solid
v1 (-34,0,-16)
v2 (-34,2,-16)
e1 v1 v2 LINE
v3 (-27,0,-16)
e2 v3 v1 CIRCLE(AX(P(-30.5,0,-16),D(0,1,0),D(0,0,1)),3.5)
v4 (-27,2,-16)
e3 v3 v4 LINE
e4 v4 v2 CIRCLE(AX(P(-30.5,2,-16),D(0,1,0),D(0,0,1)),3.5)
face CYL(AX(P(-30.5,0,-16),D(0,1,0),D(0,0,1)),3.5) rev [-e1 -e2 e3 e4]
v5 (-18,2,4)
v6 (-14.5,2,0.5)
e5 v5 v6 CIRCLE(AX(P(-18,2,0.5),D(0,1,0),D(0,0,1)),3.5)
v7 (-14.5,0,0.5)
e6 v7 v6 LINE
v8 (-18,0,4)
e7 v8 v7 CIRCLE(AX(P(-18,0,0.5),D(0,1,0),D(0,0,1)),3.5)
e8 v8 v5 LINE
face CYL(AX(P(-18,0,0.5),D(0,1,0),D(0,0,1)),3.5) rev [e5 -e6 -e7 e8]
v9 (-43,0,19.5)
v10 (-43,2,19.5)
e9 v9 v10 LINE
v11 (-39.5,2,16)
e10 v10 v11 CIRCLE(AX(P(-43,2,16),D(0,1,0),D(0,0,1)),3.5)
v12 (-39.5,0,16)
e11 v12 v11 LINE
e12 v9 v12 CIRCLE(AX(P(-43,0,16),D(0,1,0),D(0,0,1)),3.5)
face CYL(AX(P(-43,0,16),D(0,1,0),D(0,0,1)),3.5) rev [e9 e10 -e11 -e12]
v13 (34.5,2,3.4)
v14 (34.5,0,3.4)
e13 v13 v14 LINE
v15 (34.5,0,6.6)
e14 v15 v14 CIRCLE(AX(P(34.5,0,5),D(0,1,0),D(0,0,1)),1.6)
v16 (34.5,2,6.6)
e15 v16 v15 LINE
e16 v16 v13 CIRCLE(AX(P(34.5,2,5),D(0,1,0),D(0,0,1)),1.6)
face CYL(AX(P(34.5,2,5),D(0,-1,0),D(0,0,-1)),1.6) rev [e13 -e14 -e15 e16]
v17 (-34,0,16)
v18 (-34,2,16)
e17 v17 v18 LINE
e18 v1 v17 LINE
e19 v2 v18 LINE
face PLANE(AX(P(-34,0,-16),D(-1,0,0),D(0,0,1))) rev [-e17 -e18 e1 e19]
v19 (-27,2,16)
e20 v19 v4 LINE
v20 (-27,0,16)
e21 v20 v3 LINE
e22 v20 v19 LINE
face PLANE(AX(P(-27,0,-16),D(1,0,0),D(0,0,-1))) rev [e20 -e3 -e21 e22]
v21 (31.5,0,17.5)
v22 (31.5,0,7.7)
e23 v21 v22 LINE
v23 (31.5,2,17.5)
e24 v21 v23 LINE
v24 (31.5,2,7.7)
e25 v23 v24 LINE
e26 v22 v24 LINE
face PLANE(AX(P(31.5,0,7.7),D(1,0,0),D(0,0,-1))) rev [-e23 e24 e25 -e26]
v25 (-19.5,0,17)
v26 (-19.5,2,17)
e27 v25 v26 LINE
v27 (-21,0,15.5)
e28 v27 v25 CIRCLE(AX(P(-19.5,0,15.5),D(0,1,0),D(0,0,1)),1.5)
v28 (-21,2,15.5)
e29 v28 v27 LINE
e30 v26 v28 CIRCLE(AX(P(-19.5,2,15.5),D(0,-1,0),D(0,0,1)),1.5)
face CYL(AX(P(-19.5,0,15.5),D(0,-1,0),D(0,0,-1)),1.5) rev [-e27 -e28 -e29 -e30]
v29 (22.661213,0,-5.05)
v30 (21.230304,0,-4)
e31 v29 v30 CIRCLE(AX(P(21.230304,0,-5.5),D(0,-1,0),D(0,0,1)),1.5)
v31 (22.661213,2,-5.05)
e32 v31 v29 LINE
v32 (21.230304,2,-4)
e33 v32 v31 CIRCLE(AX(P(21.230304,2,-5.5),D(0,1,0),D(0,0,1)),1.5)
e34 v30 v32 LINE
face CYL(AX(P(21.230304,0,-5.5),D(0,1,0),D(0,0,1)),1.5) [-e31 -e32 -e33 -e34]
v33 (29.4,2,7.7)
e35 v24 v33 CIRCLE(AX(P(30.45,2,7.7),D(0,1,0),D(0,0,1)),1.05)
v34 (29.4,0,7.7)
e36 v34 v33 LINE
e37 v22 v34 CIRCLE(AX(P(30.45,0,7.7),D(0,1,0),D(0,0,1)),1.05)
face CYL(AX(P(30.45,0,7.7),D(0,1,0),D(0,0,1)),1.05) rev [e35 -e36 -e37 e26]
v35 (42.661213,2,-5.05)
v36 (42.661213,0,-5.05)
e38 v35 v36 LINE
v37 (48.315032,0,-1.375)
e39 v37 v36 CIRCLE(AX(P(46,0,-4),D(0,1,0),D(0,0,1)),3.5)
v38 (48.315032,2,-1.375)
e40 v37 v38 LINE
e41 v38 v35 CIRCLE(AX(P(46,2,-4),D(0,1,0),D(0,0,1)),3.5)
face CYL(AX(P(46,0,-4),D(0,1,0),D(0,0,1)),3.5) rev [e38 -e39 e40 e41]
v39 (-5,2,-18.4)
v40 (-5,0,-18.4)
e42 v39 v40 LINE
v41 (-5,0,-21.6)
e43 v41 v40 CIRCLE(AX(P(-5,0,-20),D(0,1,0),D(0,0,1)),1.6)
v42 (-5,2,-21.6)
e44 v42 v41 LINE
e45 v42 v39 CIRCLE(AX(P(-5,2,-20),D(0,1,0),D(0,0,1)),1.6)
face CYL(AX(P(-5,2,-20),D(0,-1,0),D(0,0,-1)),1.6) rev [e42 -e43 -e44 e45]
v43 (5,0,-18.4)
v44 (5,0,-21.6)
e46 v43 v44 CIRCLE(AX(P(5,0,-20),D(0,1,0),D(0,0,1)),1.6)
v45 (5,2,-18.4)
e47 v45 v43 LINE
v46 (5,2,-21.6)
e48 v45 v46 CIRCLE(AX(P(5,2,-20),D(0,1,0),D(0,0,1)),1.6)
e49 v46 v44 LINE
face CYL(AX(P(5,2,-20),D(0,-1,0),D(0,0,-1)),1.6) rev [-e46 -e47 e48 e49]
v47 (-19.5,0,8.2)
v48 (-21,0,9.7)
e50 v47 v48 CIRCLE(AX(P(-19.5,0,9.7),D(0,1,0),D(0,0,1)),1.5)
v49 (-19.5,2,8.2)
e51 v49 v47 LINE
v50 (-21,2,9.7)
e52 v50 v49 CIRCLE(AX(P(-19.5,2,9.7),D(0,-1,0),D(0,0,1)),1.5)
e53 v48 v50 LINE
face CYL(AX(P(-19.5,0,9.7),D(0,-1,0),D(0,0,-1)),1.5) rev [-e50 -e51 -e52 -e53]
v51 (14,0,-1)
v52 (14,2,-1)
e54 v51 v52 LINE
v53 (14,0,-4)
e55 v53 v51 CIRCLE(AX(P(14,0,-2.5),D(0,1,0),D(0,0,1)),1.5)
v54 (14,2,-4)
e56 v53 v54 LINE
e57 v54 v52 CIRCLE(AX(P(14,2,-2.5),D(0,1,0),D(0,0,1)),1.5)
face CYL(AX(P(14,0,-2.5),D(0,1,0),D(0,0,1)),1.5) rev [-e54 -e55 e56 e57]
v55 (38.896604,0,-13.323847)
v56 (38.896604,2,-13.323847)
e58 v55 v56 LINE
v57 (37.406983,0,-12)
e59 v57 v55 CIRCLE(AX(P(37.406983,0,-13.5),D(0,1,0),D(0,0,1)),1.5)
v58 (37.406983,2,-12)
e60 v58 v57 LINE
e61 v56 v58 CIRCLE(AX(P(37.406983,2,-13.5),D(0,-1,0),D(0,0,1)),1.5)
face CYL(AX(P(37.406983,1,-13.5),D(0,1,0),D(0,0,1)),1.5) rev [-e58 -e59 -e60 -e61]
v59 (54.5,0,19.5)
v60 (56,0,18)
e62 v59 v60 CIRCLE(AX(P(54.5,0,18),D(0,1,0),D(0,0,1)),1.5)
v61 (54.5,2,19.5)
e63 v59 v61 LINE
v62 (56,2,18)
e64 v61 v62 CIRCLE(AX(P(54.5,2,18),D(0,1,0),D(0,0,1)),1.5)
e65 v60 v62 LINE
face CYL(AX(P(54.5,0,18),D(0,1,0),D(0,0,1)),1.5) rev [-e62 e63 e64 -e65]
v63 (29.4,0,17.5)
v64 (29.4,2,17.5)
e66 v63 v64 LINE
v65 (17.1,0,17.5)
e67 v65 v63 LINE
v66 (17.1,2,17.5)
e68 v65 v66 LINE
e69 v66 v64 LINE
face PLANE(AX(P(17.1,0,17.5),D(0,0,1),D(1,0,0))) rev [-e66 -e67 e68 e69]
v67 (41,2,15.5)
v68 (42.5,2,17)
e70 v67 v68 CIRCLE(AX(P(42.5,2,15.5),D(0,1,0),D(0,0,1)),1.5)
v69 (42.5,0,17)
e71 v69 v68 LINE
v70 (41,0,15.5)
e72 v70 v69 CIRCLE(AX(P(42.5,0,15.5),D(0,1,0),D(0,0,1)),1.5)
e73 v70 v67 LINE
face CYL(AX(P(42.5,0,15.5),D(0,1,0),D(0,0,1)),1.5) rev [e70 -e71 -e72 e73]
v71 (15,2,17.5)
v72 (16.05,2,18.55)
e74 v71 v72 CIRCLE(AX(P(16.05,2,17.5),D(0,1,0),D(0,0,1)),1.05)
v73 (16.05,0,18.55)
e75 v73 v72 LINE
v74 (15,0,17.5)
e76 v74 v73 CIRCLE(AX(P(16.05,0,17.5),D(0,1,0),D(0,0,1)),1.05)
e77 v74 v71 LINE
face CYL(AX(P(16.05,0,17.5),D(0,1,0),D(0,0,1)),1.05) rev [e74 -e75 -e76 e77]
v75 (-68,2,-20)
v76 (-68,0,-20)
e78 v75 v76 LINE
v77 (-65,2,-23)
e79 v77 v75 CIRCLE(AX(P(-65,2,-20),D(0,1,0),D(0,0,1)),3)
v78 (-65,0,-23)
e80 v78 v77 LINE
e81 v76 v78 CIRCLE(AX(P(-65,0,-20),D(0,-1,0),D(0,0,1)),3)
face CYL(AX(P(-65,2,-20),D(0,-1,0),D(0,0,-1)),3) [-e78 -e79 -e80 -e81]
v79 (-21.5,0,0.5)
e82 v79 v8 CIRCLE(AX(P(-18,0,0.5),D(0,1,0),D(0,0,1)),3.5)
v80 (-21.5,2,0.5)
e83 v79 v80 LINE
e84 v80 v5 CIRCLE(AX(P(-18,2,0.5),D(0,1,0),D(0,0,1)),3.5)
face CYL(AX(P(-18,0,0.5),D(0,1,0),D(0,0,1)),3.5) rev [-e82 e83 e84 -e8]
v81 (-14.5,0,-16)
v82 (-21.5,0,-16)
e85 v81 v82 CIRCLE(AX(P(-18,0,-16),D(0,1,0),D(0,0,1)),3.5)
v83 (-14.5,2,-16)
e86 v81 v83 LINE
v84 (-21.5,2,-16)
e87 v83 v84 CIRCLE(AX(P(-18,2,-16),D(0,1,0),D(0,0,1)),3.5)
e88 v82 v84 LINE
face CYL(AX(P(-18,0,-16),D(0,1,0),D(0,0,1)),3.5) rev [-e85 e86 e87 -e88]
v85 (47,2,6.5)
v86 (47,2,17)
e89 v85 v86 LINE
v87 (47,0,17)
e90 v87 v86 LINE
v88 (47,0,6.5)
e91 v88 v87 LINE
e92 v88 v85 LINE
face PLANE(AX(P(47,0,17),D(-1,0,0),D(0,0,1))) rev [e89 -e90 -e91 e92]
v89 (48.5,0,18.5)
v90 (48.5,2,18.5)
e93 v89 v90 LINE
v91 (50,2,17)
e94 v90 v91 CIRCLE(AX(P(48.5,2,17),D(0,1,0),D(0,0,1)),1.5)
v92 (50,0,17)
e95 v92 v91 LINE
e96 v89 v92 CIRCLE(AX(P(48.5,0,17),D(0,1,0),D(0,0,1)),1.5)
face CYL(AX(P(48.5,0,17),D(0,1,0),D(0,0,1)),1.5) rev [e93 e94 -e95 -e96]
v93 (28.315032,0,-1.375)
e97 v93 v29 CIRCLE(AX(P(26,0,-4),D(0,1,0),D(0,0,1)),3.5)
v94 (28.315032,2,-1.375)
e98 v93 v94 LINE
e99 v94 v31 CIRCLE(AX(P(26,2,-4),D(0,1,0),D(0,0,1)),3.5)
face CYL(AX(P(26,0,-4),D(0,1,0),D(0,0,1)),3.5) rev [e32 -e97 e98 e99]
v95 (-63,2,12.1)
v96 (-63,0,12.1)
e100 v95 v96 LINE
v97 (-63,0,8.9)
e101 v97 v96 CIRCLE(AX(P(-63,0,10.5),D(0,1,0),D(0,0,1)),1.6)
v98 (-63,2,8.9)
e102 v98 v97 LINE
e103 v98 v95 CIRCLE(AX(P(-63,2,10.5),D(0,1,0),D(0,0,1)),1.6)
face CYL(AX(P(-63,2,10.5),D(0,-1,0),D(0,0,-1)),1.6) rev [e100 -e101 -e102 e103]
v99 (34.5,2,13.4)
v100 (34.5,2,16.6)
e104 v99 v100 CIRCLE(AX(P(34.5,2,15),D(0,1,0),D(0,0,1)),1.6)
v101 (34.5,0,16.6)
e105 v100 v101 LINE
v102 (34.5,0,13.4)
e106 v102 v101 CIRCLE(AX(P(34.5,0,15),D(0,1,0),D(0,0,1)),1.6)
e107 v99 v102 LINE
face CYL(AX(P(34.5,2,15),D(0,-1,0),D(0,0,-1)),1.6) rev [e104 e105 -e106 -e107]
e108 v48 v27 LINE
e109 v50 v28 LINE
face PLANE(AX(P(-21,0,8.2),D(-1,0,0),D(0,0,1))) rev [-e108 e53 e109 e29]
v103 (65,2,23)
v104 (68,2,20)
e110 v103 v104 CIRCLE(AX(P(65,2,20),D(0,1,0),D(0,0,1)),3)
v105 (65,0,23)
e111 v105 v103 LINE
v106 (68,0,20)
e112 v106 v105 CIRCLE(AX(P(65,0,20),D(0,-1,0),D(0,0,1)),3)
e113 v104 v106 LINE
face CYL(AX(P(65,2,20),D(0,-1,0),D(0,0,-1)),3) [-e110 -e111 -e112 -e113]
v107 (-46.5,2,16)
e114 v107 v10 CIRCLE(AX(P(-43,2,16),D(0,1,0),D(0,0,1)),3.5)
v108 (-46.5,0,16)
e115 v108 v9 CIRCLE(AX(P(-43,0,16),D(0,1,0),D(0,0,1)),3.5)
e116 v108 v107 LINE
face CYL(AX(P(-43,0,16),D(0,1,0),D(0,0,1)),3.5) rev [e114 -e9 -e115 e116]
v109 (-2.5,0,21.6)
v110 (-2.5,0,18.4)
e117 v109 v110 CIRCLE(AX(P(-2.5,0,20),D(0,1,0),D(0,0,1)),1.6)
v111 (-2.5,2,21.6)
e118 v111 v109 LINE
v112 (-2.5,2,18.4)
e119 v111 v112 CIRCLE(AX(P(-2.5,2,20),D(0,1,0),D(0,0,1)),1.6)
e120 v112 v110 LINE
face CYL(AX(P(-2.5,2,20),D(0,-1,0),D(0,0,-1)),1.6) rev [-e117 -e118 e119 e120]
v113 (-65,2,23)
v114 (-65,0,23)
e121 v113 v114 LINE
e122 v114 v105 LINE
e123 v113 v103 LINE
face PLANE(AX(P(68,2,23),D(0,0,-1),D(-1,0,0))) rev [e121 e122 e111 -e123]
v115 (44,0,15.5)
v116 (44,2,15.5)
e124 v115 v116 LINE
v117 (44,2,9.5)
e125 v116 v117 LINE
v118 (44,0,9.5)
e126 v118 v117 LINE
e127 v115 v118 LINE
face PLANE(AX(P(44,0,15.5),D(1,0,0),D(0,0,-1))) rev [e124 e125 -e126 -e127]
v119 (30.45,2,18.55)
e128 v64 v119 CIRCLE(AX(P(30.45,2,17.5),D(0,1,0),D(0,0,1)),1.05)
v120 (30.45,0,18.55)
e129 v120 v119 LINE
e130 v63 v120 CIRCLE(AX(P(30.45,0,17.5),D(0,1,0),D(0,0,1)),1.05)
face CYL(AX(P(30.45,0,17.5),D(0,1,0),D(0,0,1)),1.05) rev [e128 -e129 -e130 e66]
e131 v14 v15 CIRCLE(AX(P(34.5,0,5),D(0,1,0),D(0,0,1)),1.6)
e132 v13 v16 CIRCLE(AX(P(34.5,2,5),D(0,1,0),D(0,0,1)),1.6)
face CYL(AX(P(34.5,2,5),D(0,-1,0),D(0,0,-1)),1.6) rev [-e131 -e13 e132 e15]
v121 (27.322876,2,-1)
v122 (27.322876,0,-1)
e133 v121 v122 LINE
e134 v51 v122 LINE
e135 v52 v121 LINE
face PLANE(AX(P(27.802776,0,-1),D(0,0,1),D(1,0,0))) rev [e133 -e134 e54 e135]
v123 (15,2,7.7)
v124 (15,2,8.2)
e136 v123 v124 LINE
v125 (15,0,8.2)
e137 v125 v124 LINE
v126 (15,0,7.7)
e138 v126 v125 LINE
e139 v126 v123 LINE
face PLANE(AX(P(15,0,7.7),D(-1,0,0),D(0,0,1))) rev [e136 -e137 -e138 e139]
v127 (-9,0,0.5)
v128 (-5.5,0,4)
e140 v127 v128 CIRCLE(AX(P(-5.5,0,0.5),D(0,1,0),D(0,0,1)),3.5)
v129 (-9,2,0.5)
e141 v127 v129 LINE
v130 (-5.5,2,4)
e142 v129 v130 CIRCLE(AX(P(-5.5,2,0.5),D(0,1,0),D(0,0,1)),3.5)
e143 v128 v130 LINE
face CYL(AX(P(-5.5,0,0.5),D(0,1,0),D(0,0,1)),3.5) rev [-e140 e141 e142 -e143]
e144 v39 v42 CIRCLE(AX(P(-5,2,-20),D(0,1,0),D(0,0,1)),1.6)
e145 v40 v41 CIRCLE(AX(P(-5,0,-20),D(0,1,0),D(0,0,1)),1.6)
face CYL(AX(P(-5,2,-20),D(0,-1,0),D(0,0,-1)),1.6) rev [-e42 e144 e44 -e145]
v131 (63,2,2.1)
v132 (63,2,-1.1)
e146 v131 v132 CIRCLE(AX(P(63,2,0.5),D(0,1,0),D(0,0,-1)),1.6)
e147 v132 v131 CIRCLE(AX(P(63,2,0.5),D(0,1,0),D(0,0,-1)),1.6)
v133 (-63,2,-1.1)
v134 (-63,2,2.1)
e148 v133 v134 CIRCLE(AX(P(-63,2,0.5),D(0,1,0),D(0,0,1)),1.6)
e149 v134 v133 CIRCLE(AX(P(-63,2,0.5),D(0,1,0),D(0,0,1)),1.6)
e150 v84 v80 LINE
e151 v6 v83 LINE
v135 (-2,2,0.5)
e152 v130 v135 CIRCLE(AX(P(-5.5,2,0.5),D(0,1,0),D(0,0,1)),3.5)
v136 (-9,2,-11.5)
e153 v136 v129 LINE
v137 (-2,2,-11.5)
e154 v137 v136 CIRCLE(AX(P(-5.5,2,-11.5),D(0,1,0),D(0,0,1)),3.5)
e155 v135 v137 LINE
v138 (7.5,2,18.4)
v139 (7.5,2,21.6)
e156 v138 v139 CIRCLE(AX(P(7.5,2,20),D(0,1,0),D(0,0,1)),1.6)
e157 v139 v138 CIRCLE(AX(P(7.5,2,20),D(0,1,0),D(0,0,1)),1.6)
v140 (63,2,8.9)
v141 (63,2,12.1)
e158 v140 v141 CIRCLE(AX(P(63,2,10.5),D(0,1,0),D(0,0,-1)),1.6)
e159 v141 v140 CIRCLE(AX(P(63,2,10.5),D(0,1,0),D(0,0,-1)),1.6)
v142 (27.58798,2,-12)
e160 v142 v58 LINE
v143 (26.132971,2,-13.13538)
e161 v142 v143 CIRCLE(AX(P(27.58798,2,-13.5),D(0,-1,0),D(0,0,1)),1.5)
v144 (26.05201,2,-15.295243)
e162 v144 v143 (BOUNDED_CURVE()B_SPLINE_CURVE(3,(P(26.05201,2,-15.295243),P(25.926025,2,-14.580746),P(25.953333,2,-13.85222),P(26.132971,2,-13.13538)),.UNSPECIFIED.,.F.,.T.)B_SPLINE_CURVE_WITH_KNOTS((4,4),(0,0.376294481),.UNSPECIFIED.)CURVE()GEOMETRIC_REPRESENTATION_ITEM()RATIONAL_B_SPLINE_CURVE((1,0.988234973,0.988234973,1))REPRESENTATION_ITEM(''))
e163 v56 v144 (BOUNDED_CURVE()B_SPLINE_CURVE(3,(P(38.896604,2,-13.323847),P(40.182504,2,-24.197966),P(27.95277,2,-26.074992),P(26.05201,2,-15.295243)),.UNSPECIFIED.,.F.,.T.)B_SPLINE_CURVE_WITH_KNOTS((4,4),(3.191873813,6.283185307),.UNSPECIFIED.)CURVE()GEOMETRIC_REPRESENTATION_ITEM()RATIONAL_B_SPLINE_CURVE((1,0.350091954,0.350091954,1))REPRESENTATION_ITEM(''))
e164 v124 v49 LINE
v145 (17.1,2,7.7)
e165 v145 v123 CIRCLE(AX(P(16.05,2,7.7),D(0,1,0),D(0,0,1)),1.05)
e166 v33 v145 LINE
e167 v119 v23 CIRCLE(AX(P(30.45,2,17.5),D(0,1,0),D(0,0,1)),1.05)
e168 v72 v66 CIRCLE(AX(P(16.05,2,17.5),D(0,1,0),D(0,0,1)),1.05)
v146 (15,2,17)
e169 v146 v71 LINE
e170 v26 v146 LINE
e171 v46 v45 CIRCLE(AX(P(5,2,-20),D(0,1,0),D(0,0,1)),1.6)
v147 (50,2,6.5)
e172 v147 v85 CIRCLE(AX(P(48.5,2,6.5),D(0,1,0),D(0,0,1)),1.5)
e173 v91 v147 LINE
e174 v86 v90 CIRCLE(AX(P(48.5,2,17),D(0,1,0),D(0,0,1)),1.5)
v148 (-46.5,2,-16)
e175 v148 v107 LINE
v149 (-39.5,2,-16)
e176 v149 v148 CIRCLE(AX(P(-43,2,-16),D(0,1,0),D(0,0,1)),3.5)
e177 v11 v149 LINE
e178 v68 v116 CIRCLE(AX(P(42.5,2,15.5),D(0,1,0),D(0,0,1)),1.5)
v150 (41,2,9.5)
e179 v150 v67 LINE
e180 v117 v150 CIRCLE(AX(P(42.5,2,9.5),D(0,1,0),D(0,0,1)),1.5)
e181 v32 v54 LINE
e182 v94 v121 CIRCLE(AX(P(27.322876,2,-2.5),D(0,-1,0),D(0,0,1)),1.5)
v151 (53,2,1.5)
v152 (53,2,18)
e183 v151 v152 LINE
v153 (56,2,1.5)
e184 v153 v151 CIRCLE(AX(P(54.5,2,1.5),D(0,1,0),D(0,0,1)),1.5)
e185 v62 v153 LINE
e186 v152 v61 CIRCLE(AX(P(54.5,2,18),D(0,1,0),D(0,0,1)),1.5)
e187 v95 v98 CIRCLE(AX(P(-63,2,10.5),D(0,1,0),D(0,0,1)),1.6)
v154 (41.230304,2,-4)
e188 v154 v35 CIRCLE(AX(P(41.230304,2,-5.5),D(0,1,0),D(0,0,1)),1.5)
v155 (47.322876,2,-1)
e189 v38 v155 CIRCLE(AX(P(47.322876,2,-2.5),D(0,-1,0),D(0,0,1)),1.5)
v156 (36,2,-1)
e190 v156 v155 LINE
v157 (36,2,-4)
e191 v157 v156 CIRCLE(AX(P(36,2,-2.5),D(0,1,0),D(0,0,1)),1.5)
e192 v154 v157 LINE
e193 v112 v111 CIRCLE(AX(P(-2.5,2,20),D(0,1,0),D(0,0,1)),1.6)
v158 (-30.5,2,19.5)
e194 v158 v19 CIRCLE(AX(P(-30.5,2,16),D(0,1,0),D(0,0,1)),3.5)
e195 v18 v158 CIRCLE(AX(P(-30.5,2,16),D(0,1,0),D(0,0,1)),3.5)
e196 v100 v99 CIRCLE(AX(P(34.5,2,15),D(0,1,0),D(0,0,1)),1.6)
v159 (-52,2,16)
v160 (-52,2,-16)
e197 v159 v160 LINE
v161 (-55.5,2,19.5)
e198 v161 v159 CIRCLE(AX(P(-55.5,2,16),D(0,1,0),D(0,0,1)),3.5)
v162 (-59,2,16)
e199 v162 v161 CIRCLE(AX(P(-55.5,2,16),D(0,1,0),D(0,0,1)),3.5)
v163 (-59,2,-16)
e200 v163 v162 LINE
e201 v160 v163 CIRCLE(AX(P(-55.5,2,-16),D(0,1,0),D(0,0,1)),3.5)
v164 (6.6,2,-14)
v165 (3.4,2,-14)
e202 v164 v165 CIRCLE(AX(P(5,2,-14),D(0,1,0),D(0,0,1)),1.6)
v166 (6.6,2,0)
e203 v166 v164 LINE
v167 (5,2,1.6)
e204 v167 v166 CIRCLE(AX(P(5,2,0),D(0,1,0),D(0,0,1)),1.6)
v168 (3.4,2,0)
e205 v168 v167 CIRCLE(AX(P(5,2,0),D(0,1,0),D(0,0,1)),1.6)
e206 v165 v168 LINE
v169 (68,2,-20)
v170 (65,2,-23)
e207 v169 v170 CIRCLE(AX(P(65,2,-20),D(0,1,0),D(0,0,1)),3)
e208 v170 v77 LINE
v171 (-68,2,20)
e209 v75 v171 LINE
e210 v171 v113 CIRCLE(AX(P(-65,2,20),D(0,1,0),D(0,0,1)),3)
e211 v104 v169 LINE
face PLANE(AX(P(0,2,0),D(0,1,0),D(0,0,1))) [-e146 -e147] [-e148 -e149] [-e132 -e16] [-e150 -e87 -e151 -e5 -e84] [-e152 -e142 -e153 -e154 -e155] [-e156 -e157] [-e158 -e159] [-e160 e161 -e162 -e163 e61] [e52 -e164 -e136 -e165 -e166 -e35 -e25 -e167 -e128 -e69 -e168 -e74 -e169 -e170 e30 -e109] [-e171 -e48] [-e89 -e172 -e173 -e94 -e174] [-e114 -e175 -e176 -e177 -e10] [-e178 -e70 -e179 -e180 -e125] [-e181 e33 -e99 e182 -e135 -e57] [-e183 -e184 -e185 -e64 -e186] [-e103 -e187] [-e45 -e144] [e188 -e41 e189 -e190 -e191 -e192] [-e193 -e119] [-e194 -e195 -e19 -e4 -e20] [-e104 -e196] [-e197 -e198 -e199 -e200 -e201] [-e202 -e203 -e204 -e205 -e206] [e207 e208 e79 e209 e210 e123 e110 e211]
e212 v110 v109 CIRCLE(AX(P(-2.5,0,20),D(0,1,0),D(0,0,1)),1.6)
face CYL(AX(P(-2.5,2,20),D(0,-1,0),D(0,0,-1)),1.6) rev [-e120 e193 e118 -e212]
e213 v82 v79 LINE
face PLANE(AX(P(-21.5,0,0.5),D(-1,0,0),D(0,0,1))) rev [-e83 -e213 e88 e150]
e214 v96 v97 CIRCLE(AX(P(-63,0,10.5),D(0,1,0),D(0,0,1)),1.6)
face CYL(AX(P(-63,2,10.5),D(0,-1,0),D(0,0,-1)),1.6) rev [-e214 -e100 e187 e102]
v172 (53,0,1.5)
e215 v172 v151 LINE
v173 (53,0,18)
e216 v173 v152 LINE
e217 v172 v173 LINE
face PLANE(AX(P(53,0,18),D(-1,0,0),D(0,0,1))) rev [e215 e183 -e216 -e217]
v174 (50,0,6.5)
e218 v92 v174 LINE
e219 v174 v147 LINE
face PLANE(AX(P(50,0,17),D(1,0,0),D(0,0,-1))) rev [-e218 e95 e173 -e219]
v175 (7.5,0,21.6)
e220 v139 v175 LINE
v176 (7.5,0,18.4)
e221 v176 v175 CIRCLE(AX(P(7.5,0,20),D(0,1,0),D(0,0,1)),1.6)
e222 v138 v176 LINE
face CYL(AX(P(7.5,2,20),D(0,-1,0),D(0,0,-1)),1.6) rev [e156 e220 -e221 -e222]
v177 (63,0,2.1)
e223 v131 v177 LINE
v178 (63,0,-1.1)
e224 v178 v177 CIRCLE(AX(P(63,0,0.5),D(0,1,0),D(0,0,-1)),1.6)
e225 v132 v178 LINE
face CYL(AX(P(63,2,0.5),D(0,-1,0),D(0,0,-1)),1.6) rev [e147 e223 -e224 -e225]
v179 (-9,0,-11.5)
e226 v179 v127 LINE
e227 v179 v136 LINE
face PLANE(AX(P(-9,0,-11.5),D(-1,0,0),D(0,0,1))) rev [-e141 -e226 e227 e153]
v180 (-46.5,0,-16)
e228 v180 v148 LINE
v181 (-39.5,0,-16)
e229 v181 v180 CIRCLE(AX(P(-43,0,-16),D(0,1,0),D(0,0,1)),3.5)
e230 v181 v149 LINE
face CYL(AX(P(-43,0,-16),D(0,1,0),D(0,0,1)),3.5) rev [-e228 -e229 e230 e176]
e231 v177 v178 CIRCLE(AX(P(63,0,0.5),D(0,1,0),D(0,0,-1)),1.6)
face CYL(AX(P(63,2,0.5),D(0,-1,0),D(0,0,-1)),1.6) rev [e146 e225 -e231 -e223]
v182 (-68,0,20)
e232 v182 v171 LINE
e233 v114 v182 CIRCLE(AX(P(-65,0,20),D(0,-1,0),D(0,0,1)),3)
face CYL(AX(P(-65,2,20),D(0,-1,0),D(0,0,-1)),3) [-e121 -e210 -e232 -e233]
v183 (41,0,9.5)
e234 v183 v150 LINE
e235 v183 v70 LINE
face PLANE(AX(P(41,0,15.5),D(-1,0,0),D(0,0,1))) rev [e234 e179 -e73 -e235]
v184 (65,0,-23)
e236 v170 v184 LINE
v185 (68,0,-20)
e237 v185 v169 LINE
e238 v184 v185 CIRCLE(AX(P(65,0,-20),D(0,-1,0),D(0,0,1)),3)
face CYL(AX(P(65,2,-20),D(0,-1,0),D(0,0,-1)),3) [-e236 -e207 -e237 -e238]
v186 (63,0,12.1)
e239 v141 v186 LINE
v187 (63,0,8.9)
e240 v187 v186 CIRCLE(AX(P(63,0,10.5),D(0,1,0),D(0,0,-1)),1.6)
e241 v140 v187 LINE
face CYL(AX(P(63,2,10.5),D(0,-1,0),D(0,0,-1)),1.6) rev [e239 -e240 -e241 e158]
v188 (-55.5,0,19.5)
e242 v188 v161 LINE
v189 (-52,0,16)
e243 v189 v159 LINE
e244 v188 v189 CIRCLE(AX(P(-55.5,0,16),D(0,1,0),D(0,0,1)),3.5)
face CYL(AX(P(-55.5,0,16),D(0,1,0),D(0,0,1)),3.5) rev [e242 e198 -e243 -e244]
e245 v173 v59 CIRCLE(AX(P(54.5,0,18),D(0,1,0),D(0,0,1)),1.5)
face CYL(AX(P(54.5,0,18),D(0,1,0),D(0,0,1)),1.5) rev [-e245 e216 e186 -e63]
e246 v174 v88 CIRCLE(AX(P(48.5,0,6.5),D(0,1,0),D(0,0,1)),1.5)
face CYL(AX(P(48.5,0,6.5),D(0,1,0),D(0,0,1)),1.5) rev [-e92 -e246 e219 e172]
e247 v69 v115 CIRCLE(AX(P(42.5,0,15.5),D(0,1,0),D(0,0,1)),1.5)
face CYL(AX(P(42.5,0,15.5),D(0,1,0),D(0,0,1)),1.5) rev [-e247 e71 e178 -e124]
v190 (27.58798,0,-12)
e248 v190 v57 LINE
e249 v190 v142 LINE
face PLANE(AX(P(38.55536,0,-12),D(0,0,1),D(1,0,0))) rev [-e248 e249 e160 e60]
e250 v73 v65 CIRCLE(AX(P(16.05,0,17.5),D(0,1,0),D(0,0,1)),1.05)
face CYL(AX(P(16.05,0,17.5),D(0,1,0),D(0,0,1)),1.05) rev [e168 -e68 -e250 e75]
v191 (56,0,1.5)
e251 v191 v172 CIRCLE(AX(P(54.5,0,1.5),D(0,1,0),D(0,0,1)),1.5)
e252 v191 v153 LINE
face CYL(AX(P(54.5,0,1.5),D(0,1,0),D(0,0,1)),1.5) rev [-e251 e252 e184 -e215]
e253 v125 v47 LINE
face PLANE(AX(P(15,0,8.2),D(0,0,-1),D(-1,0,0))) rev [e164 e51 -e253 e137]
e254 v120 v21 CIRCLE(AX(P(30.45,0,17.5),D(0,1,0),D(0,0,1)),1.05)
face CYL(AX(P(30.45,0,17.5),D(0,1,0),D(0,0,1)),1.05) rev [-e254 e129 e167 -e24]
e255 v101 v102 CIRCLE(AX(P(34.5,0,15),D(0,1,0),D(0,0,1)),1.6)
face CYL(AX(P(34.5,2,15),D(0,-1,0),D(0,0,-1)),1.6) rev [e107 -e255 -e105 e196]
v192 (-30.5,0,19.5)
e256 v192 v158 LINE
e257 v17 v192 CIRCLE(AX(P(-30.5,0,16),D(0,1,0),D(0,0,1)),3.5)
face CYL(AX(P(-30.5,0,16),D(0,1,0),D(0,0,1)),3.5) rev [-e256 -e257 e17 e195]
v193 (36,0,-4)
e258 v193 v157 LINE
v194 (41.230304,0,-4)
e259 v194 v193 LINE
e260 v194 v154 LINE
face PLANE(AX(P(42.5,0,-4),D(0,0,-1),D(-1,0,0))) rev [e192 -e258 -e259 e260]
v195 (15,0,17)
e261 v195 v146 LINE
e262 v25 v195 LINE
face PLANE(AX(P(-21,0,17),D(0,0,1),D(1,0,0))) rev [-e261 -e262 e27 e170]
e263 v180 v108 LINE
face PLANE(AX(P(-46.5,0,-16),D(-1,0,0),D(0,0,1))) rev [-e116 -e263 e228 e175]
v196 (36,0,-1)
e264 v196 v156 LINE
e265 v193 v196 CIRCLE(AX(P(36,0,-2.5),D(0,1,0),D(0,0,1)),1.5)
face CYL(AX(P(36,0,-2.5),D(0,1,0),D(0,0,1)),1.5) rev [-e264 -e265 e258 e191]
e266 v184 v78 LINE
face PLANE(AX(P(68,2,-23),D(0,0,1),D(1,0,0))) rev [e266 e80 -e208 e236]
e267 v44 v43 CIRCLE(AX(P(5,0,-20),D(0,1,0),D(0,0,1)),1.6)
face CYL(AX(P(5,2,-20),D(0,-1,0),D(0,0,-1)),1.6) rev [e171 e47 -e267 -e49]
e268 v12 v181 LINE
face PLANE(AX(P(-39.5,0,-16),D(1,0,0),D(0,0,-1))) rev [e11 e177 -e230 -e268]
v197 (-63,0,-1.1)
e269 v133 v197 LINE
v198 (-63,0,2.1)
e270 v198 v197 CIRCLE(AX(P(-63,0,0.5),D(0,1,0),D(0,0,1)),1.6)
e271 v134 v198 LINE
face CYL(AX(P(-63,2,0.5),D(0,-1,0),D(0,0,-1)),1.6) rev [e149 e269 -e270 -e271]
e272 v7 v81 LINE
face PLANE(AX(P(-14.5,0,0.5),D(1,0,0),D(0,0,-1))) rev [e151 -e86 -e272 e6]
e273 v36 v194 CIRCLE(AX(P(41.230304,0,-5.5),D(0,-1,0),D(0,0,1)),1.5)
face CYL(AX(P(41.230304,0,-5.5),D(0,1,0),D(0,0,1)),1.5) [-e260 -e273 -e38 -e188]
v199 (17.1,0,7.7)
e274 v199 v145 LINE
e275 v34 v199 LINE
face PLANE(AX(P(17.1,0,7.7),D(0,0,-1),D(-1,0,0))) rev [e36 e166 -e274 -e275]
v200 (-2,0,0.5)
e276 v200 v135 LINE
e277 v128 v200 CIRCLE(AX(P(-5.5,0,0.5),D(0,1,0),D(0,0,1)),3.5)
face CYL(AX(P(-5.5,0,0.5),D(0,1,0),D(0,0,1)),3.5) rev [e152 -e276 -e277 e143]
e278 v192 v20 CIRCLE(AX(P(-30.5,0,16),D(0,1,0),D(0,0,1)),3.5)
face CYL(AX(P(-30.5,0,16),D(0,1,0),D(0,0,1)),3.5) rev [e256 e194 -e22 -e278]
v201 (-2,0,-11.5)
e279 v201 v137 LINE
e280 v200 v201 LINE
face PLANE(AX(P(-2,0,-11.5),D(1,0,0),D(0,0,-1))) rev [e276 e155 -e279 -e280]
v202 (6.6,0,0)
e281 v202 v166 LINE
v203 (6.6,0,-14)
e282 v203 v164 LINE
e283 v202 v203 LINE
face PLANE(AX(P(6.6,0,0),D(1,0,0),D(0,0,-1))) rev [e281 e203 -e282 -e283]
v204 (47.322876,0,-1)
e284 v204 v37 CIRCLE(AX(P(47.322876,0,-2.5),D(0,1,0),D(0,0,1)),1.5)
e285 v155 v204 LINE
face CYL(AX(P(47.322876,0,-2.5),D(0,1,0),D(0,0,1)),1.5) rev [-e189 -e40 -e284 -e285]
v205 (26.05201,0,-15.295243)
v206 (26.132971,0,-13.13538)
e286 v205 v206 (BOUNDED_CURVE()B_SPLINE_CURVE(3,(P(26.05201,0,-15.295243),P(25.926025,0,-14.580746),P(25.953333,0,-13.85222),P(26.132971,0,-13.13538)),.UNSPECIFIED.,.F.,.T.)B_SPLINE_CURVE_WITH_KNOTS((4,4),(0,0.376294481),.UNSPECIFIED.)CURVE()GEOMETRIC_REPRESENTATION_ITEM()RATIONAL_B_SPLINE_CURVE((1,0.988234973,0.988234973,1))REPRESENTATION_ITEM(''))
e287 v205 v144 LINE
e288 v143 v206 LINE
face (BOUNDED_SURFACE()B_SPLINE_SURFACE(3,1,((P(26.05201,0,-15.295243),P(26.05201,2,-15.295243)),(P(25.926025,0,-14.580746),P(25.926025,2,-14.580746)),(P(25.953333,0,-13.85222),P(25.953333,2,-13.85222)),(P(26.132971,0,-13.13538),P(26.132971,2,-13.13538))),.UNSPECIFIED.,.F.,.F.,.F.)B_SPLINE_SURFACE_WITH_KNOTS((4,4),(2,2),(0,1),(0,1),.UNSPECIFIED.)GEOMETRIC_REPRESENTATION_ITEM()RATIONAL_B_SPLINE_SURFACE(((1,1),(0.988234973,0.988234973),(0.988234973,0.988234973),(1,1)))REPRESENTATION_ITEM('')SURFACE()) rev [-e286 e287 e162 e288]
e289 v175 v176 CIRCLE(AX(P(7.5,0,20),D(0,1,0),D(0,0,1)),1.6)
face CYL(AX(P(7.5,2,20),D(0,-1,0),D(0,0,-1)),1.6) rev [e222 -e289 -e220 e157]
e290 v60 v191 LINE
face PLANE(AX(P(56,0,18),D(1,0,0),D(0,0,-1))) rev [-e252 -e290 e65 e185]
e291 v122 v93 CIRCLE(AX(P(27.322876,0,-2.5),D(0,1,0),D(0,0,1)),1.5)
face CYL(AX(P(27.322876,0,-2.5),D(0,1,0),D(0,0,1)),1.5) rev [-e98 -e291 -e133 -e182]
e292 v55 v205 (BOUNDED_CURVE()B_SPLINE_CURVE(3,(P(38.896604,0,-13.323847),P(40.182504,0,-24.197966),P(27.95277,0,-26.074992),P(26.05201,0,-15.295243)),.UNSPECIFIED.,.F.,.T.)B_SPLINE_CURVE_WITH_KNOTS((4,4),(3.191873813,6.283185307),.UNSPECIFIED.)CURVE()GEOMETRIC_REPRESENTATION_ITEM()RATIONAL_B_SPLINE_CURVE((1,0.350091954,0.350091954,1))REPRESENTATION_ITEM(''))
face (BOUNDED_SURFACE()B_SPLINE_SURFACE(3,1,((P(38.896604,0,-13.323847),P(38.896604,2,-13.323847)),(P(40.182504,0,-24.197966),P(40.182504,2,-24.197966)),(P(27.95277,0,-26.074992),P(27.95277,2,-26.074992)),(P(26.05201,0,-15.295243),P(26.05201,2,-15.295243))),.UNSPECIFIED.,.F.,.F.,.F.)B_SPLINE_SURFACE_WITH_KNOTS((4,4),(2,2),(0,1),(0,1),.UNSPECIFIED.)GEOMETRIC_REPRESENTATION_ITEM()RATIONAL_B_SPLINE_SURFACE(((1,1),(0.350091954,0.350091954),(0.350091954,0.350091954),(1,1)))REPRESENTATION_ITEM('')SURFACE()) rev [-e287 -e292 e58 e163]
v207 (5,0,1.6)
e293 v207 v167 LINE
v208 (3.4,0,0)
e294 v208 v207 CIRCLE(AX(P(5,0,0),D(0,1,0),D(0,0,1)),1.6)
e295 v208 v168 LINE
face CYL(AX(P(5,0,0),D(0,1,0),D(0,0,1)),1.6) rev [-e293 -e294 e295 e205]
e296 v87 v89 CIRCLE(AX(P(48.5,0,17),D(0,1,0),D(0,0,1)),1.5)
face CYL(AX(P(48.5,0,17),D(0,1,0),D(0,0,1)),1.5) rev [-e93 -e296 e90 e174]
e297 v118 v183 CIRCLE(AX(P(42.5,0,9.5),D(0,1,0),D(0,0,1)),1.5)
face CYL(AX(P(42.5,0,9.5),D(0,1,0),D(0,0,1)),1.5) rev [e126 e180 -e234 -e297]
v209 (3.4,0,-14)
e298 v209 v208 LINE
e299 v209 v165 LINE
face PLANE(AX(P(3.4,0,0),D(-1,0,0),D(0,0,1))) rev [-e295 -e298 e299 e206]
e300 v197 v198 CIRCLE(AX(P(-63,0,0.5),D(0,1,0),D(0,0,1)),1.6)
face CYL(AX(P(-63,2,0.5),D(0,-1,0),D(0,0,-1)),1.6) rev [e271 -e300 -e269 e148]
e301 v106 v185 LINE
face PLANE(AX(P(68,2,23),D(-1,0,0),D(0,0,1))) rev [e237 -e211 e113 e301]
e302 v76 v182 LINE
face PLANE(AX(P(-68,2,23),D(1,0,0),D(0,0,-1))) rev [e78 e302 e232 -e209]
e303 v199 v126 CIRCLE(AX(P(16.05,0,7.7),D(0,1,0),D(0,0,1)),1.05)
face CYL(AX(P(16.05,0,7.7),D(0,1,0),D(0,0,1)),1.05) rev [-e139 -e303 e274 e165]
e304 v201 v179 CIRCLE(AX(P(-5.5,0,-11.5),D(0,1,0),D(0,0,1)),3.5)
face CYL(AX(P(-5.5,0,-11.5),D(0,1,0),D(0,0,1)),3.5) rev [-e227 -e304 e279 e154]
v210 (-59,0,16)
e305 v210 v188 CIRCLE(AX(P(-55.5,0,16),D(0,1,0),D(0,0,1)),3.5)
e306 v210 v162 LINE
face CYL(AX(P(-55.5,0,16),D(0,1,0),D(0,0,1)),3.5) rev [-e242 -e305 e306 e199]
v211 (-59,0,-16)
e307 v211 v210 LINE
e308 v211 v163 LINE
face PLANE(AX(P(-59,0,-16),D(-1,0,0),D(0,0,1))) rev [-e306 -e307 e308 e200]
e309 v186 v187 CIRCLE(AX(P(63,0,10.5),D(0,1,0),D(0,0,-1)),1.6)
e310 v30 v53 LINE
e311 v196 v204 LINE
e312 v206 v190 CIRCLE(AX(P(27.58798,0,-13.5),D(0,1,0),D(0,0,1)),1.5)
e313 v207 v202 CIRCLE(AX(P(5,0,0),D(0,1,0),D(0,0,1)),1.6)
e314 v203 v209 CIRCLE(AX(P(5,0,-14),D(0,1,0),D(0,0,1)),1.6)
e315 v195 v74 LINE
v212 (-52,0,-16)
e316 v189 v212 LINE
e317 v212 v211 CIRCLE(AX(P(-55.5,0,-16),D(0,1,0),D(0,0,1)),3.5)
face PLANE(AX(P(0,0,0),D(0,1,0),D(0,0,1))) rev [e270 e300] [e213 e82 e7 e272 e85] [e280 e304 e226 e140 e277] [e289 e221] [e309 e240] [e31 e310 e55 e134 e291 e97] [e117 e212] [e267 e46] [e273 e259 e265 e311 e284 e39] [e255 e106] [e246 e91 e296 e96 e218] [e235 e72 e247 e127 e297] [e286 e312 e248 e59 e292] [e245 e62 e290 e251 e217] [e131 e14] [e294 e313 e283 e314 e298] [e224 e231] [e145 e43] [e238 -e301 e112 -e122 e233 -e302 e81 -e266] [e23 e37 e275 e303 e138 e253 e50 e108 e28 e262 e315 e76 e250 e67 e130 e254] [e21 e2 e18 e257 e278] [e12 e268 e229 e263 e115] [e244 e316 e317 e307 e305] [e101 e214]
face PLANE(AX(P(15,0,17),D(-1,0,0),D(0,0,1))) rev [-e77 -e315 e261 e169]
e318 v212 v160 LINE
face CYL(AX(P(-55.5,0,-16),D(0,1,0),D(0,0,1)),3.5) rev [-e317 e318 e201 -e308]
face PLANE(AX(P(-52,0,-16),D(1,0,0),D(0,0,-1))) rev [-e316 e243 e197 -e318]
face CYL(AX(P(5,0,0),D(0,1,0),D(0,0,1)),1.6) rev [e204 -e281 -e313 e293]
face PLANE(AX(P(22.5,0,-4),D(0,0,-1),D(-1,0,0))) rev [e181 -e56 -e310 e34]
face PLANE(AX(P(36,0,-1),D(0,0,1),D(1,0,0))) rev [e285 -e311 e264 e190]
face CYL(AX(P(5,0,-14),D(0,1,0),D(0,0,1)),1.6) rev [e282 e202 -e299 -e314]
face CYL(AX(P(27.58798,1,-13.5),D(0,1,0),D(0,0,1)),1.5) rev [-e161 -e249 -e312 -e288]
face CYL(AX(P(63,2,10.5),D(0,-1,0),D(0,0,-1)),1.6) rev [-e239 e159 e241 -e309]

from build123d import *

# Parameters (mm, degrees)
SKETCH_1_W          = 136
SKETCH_1_H          = 46
SKETCH_1_R          = 1.6
EXTRUDE_1_DEPTH     = 2
CUT_EXTRUDE_1_DEPTH = 72.812255222
FILLET_R1_5_R       = 1.5
FILLET_R3_R         = 3


with BuildPart() as part:
    # 草图1 → 凸台-拉伸1 (new body)
    with BuildSketch(Plane(origin=(0, 0, 0), x_dir=(1, 0, 0), z_dir=(0, 1, 0))):
        Rectangle(SKETCH_1_W, SKETCH_1_H)
        with Locations(Location((-63, -0.5, 0), (0, 0, 270))):
            Circle(SKETCH_1_R, mode=Mode.SUBTRACT)
        with Locations(Location((-63, -10.5, 0), (0, 0, 270))):
            Circle(SKETCH_1_R, mode=Mode.SUBTRACT)
        with Locations(Location((-2.5, -20, 0), (0, 0, 270))):
            Circle(SKETCH_1_R, mode=Mode.SUBTRACT)
        with Locations(Location((7.5, -20, 0), (0, 0, 270))):
            Circle(SKETCH_1_R, mode=Mode.SUBTRACT)
        with Locations(Location((63, -10.5, 0), (0, 0, 90))):
            Circle(SKETCH_1_R, mode=Mode.SUBTRACT)
        with Locations(Location((63, -0.5, 0), (0, 0, 90))):
            Circle(SKETCH_1_R, mode=Mode.SUBTRACT)
        with Locations(Location((5, 20, 0), (0, 0, 270))):
            Circle(SKETCH_1_R, mode=Mode.SUBTRACT)
        with Locations(Location((-5, 20, 0), (0, 0, 270))):
            Circle(SKETCH_1_R, mode=Mode.SUBTRACT)
        with Locations(Location((34.5, -5, 0), (0, 0, 270))):
            Circle(SKETCH_1_R, mode=Mode.SUBTRACT)
        with Locations(Location((34.5, -15, 0), (0, 0, 270))):
            Circle(SKETCH_1_R, mode=Mode.SUBTRACT)
    extrude(amount=EXTRUDE_1_DEPTH)

    # 草图2 → 切除-拉伸1 (cut, through all)
    with BuildSketch(Plane(origin=(0, 2, 0), x_dir=(1, 0, 0), z_dir=(0, 1, 0))):
        with BuildLine():
            Line((-52, 16), (-52, -16))
            ThreePointArc((-52, -16), (-55.5, -19.5), (-59, -16))
            Line((-59, -16), (-59, 16))
            ThreePointArc((-59, 16), (-55.5, 19.5), (-52, 16))
        make_face()
        with BuildLine():
            Line((17.1, -7.7), (29.4, -7.7))
            ThreePointArc((29.4, -7.7), (30.45, -6.65), (31.5, -7.7))
            Line((31.5, -7.7), (31.5, -17.5))
            ThreePointArc((31.5, -17.5), (30.45, -18.55), (29.4, -17.5))
            Line((29.4, -17.5), (17.1, -17.5))
            ThreePointArc((17.1, -17.5), (16.05, -18.55), (15, -17.5))
            Line((15, -17.5), (15, -17))
            Line((15, -17), (-21, -17))
            Line((-21, -17), (-21, -8.2))
            Line((-21, -8.2), (15, -8.2))
            Line((15, -8.2), (15, -7.7))
            ThreePointArc((15, -7.7), (16.05, -6.65), (17.1, -7.7))
        make_face()
        with BuildLine():
            Line((-39.5, 16), (-39.5, -16))
            ThreePointArc((-39.5, -16), (-43, -19.5), (-46.5, -16))
            Line((-46.5, -16), (-46.5, 16))
            ThreePointArc((-46.5, 16), (-43, 19.5), (-39.5, 16))
        make_face()
        with BuildLine():
            Line((-27, 16), (-27, -16))
            ThreePointArc((-27, -16), (-30.5, -19.5), (-34, -16))
            Line((-34, -16), (-34, 16))
            ThreePointArc((-34, 16), (-30.5, 19.5), (-27, 16))
        make_face()
        with BuildLine():
            Line((-2, 11.5), (-2, -0.5))
            ThreePointArc((-2, -0.5), (-5.5, -4), (-9, -0.5))
            Line((-9, -0.5), (-9, 11.5))
            ThreePointArc((-9, 11.5), (-5.5, 15), (-2, 11.5))
        make_face()
        with BuildLine():
            Line((42.5, 4), (36, 4))
            ThreePointArc((36, 4), (34.5, 2.5), (36, 1))
            Line((36, 1), (47.802775638, 1))
            ThreePointArc((47.802775638, 1), (47.723410176, 7.046285831), (42.5, 4))
        make_face()
        with BuildLine():
            Line((41, -15.5), (41, -9.5))
            ThreePointArc((41, -9.5), (42.5, -8), (44, -9.5))
            Line((44, -9.5), (44, -15.5))
            ThreePointArc((44, -15.5), (42.5, -17), (41, -15.5))
        make_face()
        with BuildLine():
            Line((47, -17), (47, -6.5))
            ThreePointArc((47, -6.5), (48.5, -5), (50, -6.5))
            Line((50, -6.5), (50, -17))
            ThreePointArc((50, -17), (48.5, -18.5), (47, -17))
        make_face()
        with BuildLine():
            Line((53, -18), (53, -1.5))
            ThreePointArc((53, -1.5), (54.5, 0), (56, -1.5))
            Line((56, -1.5), (56, -18))
            ThreePointArc((56, -18), (54.5, -19.5), (53, -18))
        make_face()
        with BuildLine():
            Line((22.5, 4), (14, 4))
            ThreePointArc((14, 4), (12.5, 2.5), (14, 1))
            Line((14, 1), (27.802775638, 1))
            ThreePointArc((27.802775638, 1), (27.723410176, 7.046285831), (22.5, 4))
        make_face()
        with BuildLine():
            Line((38.555359619, 12), (26.555359619, 12))
            add(Edge.make_bspline(
                [(38.555359619, 12), (41.784518916, 19.940569638), (32.181153285, 19.940569638), (22.577787653, 19.940569638), (26.555359619, 12)],
                knots=[6.095299784, 6.095299784, 6.095299784, 8.050729179, 8.050729179, 10.006158574, 10.006158574, 10.006158574], degree=2, weights=[1, 0.558919028, 1, 0.558919028, 1]))
        make_face()
        with BuildLine():
            Line((3.4, 0), (3.4, 14))
            ThreePointArc((3.4, 14), (5, 15.6), (6.6, 14))
            Line((6.6, 14), (6.6, 0))
            ThreePointArc((6.6, 0), (5, -1.6), (3.4, 0))
        make_face()
        with BuildLine():
            Line((-21.5, -0.5), (-21.5, 16))
            ThreePointArc((-21.5, 16), (-18, 19.5), (-14.5, 16))
            Line((-14.5, 16), (-14.5, -0.5))
            ThreePointArc((-14.5, -0.5), (-18, -4), (-21.5, -0.5))
        make_face()
    extrude(amount=-CUT_EXTRUDE_1_DEPTH, mode=Mode.SUBTRACT)

    # R1.5 镂空圆角
    fillet_r1_5_edges = [part.edges().sort_by_distance(p)[0] for p in [
        (-21, 1, 8.2),
        (-21, 1, 17),
        (38.555359619, 1, -12),
        (26.555359619, 1, -12),
        (22.5, 1, -4),
        (27.802775638, 1, -1),
        (42.5, 1, -4),
        (47.802775638, 1, -1),
    ]]
    fillet(fillet_r1_5_edges, radius=FILLET_R1_5_R)

    # R3 外缘圆角
    fillet_r3_edges = [part.edges().sort_by_distance(p)[0] for p in [
        (-68, 1, -23),
        (68, 1, -23),
        (68, 1, 23),
        (-68, 1, 23),
    ]]
    fillet(fillet_r3_edges, radius=FILLET_R3_R)


solid = part.part
